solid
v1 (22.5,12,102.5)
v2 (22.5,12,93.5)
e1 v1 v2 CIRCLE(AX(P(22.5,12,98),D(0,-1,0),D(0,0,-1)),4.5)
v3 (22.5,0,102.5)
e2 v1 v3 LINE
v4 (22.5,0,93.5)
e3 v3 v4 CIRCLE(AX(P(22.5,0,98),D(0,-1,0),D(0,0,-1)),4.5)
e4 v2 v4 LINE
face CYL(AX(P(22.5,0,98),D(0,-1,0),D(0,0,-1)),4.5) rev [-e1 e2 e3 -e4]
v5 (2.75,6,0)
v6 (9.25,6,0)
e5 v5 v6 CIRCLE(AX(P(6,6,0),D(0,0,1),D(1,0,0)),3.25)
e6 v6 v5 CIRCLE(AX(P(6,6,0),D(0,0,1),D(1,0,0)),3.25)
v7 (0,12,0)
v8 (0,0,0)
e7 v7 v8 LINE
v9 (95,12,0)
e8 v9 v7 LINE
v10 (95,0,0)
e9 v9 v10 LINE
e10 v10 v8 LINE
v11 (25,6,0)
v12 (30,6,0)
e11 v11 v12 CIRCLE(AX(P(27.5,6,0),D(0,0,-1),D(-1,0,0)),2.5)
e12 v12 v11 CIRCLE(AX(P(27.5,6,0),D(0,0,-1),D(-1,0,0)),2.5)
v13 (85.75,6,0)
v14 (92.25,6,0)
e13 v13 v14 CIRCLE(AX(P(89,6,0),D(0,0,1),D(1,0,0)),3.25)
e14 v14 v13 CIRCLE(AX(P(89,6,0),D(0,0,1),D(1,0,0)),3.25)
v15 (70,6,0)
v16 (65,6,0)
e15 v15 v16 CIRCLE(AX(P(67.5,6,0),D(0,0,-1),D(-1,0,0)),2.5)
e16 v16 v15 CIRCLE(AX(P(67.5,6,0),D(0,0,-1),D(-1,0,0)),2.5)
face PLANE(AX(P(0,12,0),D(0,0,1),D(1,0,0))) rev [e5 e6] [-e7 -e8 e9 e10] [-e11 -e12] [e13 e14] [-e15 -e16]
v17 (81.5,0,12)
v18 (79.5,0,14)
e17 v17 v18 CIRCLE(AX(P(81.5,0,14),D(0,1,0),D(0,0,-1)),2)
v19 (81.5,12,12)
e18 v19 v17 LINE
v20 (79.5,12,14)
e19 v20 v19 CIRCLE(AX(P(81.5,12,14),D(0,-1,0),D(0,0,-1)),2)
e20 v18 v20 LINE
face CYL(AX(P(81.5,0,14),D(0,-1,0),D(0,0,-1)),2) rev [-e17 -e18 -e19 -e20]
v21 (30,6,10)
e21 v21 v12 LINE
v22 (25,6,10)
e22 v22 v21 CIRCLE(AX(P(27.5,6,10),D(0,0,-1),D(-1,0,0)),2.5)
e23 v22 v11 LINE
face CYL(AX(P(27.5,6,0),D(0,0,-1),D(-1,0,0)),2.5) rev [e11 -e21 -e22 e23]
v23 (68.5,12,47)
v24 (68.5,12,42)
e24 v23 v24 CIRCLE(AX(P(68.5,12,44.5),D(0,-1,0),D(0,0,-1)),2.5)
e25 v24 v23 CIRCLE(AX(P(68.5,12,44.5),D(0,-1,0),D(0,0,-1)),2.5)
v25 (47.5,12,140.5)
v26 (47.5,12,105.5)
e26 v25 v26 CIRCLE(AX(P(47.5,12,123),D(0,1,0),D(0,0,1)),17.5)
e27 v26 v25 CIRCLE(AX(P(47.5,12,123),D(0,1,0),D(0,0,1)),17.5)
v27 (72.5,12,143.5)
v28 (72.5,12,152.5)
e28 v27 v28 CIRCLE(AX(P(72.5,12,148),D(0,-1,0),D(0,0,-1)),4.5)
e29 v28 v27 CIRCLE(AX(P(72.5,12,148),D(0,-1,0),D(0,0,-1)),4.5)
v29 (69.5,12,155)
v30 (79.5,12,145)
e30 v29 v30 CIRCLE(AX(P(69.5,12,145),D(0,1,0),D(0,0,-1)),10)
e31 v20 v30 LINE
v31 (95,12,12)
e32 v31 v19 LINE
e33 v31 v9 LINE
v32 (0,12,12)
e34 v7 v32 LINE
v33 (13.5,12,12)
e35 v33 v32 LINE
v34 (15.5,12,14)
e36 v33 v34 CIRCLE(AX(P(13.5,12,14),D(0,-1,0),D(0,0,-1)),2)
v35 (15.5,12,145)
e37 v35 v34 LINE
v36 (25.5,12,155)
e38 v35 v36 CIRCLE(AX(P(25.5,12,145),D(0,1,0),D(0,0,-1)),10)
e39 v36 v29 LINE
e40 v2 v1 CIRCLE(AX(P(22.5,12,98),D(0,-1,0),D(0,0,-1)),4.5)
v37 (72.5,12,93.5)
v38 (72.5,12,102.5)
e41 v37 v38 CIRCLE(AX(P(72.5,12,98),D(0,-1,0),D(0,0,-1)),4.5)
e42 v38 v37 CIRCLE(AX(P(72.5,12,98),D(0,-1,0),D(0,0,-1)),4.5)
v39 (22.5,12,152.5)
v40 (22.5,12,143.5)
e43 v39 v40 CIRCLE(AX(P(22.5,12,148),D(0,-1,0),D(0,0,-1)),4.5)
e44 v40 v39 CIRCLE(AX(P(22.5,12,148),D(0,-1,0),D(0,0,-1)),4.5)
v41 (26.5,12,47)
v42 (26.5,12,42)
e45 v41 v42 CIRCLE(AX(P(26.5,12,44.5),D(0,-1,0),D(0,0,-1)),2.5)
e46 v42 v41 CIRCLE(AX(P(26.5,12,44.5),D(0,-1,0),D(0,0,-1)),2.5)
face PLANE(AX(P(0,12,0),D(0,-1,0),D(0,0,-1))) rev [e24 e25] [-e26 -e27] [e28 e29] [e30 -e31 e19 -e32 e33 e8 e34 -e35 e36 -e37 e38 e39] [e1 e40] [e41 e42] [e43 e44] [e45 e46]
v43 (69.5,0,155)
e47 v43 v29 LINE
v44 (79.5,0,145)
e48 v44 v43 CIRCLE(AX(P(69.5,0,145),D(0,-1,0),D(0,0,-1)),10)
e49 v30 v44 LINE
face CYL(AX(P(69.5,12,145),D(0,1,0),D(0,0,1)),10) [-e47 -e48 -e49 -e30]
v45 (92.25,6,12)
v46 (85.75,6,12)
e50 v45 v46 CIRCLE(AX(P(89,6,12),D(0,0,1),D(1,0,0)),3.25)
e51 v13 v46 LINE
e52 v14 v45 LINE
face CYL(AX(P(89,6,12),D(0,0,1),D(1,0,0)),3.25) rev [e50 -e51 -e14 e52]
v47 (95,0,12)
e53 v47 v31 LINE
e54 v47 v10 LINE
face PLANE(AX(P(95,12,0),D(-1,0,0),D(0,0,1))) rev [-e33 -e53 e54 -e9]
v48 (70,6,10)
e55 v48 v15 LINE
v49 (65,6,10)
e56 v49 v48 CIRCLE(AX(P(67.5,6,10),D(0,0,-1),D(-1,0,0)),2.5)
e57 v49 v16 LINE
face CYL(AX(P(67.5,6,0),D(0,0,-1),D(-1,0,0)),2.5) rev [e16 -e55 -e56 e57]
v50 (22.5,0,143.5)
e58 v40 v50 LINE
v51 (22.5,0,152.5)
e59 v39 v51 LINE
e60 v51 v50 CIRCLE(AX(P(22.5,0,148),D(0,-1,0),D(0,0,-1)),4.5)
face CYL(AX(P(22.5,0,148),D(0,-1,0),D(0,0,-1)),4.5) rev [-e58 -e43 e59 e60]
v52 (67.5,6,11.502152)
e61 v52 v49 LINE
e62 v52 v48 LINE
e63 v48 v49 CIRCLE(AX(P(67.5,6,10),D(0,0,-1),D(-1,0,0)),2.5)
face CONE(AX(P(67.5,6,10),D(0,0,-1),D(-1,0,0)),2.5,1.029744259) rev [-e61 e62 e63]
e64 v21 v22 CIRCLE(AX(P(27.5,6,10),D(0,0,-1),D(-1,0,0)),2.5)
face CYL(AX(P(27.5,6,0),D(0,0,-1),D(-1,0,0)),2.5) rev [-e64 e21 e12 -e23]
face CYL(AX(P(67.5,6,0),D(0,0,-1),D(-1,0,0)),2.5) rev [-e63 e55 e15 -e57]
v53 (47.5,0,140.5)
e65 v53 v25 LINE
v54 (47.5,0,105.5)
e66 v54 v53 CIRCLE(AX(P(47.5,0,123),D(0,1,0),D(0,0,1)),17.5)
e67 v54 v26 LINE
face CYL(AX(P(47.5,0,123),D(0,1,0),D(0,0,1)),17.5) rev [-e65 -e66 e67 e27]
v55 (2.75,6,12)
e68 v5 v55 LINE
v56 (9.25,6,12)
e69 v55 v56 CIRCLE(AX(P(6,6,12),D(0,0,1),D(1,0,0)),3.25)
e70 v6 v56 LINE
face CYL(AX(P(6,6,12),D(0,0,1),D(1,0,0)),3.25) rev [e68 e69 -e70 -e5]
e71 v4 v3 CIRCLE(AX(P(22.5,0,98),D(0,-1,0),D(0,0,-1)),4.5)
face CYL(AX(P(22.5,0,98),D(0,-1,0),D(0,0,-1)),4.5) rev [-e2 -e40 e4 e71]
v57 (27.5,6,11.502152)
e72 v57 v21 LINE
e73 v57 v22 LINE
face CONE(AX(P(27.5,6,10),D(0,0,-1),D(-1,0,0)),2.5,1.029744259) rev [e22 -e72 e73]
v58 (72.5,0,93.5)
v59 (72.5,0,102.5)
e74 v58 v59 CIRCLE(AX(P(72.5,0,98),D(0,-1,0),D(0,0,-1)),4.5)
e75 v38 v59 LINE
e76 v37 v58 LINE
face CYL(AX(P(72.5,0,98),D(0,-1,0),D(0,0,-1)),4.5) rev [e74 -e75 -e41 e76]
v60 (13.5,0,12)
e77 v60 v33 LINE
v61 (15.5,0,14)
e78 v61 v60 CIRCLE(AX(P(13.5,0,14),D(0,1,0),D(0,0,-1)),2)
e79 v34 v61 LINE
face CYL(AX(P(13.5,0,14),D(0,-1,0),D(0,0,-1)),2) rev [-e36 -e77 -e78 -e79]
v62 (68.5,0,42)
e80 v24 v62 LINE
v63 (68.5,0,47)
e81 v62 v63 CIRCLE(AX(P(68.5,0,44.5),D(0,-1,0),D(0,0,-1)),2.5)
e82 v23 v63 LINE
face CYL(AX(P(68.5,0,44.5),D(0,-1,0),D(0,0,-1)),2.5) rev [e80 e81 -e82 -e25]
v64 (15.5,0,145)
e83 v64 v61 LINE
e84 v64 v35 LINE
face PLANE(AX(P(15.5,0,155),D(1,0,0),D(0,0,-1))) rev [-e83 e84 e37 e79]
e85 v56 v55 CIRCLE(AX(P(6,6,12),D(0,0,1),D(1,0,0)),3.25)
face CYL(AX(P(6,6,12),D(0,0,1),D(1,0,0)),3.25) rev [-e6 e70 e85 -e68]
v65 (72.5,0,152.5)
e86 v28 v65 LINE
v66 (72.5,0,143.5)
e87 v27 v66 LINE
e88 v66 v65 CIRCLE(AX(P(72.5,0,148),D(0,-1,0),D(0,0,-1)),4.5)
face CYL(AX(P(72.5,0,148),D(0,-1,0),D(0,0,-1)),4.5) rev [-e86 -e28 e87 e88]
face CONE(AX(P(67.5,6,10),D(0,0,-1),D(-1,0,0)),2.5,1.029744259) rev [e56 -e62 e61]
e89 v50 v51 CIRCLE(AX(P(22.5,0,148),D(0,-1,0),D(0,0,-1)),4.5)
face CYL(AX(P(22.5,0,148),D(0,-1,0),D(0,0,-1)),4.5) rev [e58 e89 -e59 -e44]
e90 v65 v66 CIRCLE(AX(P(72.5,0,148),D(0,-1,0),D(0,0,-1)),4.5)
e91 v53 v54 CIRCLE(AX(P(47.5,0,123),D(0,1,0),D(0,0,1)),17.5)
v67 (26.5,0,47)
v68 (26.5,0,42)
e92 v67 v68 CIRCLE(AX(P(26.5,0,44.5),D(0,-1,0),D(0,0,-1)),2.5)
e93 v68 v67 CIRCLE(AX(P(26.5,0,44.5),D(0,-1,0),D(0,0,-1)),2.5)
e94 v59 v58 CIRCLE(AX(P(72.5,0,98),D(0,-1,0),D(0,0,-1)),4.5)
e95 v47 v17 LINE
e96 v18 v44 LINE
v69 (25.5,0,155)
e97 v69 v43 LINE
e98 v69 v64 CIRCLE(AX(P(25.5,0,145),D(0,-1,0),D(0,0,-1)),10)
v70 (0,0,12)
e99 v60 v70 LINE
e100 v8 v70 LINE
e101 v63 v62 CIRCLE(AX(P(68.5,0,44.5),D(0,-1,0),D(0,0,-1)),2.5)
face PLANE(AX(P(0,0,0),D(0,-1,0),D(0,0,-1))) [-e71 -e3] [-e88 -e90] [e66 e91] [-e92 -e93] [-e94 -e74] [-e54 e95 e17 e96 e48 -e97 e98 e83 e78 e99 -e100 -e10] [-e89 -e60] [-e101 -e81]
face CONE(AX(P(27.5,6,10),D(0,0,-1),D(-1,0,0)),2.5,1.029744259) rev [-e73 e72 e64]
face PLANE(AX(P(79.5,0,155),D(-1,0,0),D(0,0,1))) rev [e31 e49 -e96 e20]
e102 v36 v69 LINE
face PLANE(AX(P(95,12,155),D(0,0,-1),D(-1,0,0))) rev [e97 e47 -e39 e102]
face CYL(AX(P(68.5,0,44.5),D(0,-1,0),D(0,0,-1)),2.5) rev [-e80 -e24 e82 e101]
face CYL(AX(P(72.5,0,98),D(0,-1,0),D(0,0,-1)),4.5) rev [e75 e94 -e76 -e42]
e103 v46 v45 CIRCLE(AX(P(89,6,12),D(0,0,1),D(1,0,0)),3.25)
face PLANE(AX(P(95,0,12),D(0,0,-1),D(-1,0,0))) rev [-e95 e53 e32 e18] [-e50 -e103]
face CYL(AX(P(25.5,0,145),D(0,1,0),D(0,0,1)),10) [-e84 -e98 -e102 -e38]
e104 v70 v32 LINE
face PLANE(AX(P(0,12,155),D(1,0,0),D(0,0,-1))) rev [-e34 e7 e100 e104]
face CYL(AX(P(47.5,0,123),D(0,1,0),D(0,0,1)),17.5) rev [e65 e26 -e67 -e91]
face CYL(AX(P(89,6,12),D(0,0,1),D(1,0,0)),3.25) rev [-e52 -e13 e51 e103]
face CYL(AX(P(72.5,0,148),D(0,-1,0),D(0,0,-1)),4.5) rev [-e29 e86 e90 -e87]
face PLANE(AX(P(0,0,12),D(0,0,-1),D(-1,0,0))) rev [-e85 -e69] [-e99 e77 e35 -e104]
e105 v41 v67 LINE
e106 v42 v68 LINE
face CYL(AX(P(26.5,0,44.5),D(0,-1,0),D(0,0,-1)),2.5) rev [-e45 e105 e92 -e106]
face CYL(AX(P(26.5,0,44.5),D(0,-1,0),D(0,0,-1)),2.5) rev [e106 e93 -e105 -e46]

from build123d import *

# Parameters (mm, degrees)
SKETCH_1_W                = 95
SKETCH_1_H                = 155
EXTRUDE_1_DEPTH           = 12
SKETCH_9_W                = 15.5
SKETCH_9_H                = 143
CUT_EXTRUDE_4_DEPTH       = 183.1922062
HOLE_WIZARD_6_5_6_5_1_D   = 6.5
SKETCH_12_R               = 17.5
CUT_EXTRUDE_5_DEPTH       = 183.1922062
FILLET_1_R                = 10
HOLE_WIZARD_5_0_5_1_D     = 5
HOLE_WIZARD_5_0_5_1_DEPTH = 10
HOLE_WIZARD_5_0_5_1_TIP   = 1.502151548
FILLET_2_R                = 2
HOLE_WIZARD_M6_2_D        = 5
MM_1_D                    = 9


with BuildPart() as part:
    # 草图1 → 凸台-拉伸1 (new body)
    with BuildSketch(Plane(origin=(0, 0, 0), x_dir=(1, 0, 0), z_dir=(0, 1, 0))):
        with Locations((47.5, -77.5)):
            Rectangle(SKETCH_1_W, SKETCH_1_H)
    extrude(amount=EXTRUDE_1_DEPTH)

    # 草图9 → 切除-拉伸4 (cut, through all)
    with BuildSketch(Plane(origin=(0, 12, 0), x_dir=(1, 0, 0), z_dir=(0, 1, 0))):
        with Locations((7.75, -83.5)):
            Rectangle(SKETCH_9_W, SKETCH_9_H)
        with Locations((87.25, -83.5)):
            Rectangle(SKETCH_9_W, SKETCH_9_H)
    extrude(amount=-CUT_EXTRUDE_4_DEPTH, mode=Mode.SUBTRACT)

    # Ø6.5 (6.5) 直径孔1 (through all)
    with Locations(Plane.XY.offset(12)):
        with Locations((6, 6), (89, 6)):
            Hole(HOLE_WIZARD_6_5_6_5_1_D / 2)

    # 草图12 → 切除-拉伸5 (cut, through all)
    with BuildSketch(Plane(origin=(0, 12, 0), x_dir=(1, 0, 0), z_dir=(0, 1, 0))):
        with Locations(Location((47.5, -123, 0), (0, 0, 270))):
            Circle(SKETCH_12_R)
    extrude(amount=-CUT_EXTRUDE_5_DEPTH, mode=Mode.SUBTRACT)

    # 圆角1
    fillet_1_edges = [part.edges().sort_by_distance(p)[0] for p in [
        (15.5, 6, 155),
        (79.5, 6, 155),
    ]]
    fillet(fillet_1_edges, radius=FILLET_1_R)

    # Ø5.0 (5) 直径孔1
    with Locations(Plane(origin=(0, 0, 0), x_dir=(-1, 0, 0), z_dir=(0, 0, -1))):
        with Locations((-67.5, 6), (-27.5, 6)):
            Hole(HOLE_WIZARD_5_0_5_1_D / 2, depth=HOLE_WIZARD_5_0_5_1_DEPTH)
            with Locations((0, 0, -(HOLE_WIZARD_5_0_5_1_DEPTH + HOLE_WIZARD_5_0_5_1_TIP / 2))):  # 118° drill point
                Cone(0, HOLE_WIZARD_5_0_5_1_D / 2, HOLE_WIZARD_5_0_5_1_TIP, mode=Mode.SUBTRACT)

    # 圆角2
    fillet_2_edges = [part.edges().sort_by_distance(p)[0] for p in [
        (15.5, 6, 12),
        (79.5, 6, 12),
    ]]
    fillet(fillet_2_edges, radius=FILLET_2_R)

    # M6 螺纹孔2 (through all)
    with Locations(Plane(origin=(0, 0, 0), x_dir=(-1, 0, 0), z_dir=(0, -1, 0))):
        with Locations((-68.5, -44.5), (-26.5, -44.5)):
            Hole(HOLE_WIZARD_M6_2_D / 2)

    # 大小mm 暗销孔1 (through all)
    with Locations(Plane(origin=(0, 0, 0), x_dir=(-1, 0, 0), z_dir=(0, -1, 0))):
        with Locations((-72.5, -98), (-72.5, -148), (-22.5, -148), (-22.5, -98)):
            Hole(MM_1_D / 2)


solid = part.part
